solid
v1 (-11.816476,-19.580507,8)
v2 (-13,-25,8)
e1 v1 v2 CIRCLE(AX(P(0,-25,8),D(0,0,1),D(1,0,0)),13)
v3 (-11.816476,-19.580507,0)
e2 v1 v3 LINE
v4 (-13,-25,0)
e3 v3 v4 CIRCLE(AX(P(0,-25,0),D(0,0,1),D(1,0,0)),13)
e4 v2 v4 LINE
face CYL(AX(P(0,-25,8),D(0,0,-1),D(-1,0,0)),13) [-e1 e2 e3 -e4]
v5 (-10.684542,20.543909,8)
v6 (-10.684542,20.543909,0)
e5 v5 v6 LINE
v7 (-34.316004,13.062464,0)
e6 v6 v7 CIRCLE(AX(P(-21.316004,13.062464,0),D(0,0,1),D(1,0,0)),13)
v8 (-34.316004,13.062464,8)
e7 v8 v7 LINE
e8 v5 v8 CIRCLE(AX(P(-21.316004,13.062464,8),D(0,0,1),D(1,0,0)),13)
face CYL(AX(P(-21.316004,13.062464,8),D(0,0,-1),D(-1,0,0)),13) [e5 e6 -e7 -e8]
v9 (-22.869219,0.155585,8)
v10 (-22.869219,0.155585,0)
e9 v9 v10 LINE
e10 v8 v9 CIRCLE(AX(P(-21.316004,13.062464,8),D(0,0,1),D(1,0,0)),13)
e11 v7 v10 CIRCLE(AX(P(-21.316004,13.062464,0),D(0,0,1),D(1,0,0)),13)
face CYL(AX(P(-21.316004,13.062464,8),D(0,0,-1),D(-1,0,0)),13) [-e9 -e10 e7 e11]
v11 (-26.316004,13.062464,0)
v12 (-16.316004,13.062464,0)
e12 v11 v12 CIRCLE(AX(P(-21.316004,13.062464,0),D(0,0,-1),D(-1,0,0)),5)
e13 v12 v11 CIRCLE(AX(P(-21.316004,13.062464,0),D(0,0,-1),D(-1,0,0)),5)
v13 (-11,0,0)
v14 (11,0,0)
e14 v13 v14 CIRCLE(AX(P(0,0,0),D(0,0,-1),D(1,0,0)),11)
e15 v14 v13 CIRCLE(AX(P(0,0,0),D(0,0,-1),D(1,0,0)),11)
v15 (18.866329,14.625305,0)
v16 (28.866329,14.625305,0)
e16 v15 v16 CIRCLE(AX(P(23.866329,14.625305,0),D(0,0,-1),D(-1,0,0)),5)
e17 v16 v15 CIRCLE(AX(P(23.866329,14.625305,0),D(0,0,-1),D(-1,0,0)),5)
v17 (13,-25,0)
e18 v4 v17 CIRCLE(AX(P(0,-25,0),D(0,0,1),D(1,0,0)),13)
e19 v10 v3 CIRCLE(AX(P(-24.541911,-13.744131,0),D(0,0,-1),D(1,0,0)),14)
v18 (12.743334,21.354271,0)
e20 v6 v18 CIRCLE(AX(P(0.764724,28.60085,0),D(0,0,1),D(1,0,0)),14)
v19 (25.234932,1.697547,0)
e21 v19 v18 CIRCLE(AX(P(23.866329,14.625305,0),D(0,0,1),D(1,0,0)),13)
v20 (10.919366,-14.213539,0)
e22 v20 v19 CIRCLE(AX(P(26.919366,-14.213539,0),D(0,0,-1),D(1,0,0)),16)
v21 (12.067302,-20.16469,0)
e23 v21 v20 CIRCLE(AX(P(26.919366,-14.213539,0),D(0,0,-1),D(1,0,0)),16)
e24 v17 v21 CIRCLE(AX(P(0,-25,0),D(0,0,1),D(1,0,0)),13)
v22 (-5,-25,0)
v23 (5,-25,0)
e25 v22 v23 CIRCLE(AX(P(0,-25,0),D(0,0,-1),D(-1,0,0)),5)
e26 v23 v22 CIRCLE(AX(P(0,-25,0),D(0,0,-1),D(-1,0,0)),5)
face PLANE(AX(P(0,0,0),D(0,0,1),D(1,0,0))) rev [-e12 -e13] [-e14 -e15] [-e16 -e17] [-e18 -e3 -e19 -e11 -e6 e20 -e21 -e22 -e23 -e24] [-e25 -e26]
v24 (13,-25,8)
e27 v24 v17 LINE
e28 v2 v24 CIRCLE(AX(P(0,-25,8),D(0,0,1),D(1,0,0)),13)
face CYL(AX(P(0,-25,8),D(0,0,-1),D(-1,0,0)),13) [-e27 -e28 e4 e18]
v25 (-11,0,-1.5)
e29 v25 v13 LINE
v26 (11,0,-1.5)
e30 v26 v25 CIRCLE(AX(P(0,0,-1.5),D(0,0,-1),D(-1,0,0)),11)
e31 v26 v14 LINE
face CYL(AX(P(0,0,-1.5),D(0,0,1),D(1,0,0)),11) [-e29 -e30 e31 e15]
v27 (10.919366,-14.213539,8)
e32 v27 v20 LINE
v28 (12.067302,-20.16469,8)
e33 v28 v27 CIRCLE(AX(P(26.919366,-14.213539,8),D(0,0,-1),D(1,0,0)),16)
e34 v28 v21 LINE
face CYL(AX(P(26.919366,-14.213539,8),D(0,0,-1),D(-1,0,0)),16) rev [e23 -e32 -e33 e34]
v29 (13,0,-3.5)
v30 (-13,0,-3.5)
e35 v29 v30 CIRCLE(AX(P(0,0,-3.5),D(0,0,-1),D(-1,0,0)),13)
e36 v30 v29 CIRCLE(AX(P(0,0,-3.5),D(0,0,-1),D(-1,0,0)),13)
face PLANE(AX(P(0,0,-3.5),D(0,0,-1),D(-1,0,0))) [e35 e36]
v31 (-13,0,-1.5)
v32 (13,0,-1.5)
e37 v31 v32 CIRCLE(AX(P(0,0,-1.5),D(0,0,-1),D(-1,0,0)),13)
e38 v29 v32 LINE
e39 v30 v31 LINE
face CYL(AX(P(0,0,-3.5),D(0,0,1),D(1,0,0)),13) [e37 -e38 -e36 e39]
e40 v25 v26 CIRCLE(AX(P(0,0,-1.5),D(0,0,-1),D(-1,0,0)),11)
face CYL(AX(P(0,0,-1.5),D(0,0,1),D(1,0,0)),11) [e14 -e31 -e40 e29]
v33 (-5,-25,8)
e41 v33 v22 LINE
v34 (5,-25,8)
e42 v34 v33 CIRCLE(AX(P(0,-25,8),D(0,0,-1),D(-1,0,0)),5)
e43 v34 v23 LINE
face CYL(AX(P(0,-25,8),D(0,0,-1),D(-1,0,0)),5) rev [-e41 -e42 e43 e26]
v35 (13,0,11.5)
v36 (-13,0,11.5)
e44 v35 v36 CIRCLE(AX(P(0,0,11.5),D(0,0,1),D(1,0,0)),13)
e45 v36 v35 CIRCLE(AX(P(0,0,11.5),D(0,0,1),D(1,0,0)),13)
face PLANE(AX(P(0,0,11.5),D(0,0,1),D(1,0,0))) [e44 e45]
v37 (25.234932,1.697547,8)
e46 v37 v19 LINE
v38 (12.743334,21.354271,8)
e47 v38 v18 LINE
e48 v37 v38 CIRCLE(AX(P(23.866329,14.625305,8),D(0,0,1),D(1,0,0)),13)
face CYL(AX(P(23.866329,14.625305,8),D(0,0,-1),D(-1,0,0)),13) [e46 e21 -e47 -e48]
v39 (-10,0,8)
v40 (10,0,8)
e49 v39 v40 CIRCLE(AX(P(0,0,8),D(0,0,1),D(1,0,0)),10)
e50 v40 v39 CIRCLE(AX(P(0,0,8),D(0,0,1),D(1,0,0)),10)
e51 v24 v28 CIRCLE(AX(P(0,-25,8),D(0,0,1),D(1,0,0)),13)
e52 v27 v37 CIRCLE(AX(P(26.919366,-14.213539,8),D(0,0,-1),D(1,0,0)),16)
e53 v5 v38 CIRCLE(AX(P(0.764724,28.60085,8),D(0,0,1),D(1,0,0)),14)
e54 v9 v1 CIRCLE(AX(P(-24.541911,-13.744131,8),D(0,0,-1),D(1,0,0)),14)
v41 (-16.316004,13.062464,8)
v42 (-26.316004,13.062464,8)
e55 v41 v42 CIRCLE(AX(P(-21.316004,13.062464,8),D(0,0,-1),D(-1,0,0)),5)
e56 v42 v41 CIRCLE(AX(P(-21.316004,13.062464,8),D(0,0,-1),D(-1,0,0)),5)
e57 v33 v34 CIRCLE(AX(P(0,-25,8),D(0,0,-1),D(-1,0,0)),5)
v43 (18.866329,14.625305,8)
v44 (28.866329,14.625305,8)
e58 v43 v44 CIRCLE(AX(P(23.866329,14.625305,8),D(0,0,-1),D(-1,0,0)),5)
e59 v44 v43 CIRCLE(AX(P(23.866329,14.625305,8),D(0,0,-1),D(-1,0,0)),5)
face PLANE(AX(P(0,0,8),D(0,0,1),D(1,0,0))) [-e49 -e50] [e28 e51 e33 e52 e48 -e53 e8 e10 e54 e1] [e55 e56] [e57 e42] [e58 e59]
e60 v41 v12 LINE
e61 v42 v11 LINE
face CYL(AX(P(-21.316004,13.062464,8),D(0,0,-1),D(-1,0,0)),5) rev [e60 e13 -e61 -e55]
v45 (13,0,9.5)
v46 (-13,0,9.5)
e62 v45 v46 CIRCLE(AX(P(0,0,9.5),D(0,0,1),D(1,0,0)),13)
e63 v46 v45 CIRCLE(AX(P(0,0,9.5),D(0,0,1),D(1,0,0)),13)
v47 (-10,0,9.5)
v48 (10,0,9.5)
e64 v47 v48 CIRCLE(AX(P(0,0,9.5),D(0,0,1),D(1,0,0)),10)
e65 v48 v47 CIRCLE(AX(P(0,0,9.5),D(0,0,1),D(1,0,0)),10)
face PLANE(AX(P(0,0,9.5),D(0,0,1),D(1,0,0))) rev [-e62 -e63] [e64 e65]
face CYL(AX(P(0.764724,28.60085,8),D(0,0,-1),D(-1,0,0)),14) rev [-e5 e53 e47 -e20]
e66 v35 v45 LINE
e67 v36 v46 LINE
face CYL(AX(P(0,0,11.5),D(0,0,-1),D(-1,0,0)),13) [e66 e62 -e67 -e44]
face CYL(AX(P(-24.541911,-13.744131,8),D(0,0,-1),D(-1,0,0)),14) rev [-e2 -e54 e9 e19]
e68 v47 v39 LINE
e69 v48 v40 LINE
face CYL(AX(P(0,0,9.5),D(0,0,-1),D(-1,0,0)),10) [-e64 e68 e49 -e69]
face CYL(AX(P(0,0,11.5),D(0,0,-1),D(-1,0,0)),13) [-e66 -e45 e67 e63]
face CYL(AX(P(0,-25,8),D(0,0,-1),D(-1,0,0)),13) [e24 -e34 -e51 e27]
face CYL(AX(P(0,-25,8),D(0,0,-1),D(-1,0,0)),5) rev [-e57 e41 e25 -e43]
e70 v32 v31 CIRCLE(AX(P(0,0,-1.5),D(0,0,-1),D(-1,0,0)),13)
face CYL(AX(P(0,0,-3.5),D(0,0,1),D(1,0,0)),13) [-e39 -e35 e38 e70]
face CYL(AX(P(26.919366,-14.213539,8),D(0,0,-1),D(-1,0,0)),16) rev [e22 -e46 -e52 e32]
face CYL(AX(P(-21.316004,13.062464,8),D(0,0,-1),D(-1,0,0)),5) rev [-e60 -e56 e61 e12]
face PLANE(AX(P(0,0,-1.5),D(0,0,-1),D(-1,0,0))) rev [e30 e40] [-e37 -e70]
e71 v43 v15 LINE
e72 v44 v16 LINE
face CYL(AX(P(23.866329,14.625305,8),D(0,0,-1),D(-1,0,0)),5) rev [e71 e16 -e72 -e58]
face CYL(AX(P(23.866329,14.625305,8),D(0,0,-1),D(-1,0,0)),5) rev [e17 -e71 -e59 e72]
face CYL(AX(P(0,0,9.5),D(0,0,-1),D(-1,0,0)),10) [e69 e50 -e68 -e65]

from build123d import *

# Parameters (mm, degrees)
SPINNER_BODY_DEPTH             = 8
HUB_BOSS_10_SKETCH_R           = 10
HUB_BOSS_10_DEPTH              = 1.5
HUB_BOSS_11_SKETCH_R           = 11
HUB_BOSS_11_DEPTH              = 1.5
HUB_CAP_13_ON_11_BOSS_SKETCH_R = 13
HUB_CAP_13_ON_11_BOSS_DEPTH    = 2
HUB_START                      = 2
HUB_CAP_13_ON_10_BOSS_SKETCH_R = 13
HUB_CAP_13_ON_10_BOSS_DEPTH    = 2
LOBE_HOLES_3X_10_SKETCH_R      = 10
LOBE_HOLES_3X_10_DEPTH         = 8
LOBE_RINGS_3X_10_9_SKETCH_R    = 10
LOBE_RINGS_3X_10_9_SKETCH_R_2  = 9
LOBE_RINGS_3X_10_9_DEPTH       = 8
LOBE_RINGS_3X_9_6_SKETCH_R     = 9
LOBE_RINGS_3X_9_6_SKETCH_R_2   = 6
LOBE_RINGS_3X_9_6_DEPTH        = 8
LOBE_RINGS_3X_6_5_SKETCH_R     = 6
LOBE_RINGS_3X_6_5_SKETCH_R_2   = 5
LOBE_RINGS_3X_6_5_DEPTH        = 8


with BuildPart() as part:
    # Spinner Body Sketch → Spinner Body (new body)
    with BuildSketch(Plane.XY):
        with BuildLine():
            ThreePointArc((-11.816475763, -19.580507354), (-0.317877053, -37.996113041), (12.067302022, -20.164690091))
            ThreePointArc((12.067302022, -20.164690091), (13.213407519, -5.958437932), (25.234931886, 1.697547316))
            ThreePointArc((25.234931886, 1.697547316), (34.838281601, 21.597841349), (12.74333417, 21.35427128))
            ThreePointArc((12.74333417, 21.35427128), (1.248689911, 14.609217628), (-10.684542323, 20.543909185))
            ThreePointArc((-10.684542323, 20.543909185), (-32.475062427, 19.731453355), (-22.869218634, 0.155585152))
            ThreePointArc((-22.869218634, 0.155585152), (-12.326967101, -6.903433276), (-11.816475763, -19.580507354))
        make_face()
    extrude(amount=SPINNER_BODY_DEPTH)

    # Hub Boss Ø10 Sketch → Hub Boss Ø10 (add)
    with BuildSketch(Plane.XY.offset(8)):
        Circle(HUB_BOSS_10_SKETCH_R)
    extrude(amount=HUB_BOSS_10_DEPTH)

    # Hub Boss Ø11 Sketch → Hub Boss Ø11 (add)
    with BuildSketch(Plane(origin=(0, 0, 0), x_dir=(-1, 0, 0), z_dir=(0, 0, -1))):
        with Locations(Location((0, 0, 0), (0, 0, 180))):
            Circle(HUB_BOSS_11_SKETCH_R)
    extrude(amount=HUB_BOSS_11_DEPTH)

    # Hub Cap Ø13 on Ø11 Boss Sketch → Hub Cap Ø13 on Ø11 Boss (add)
    with BuildSketch(Plane(origin=(0, 0, -1.5), x_dir=(-1, 0, 0), z_dir=(0, 0, -1))):
        Circle(HUB_CAP_13_ON_11_BOSS_SKETCH_R)
    extrude(amount=HUB_CAP_13_ON_11_BOSS_DEPTH)

    # Hub Cap Ø13 on Ø10 Boss Sketch → Hub Cap Ø13 on Ø10 Boss (add)
    with BuildSketch(Plane.XY.offset(9.5).offset(HUB_START)):
        with Locations(Location((0, 0, 0), (0, 0, 180))):
            Circle(HUB_CAP_13_ON_10_BOSS_SKETCH_R)
    extrude(amount=-HUB_CAP_13_ON_10_BOSS_DEPTH)

    # Lobe Holes 3xØ10 Sketch → Lobe Holes 3xØ10 (cut)
    with BuildSketch(Plane(origin=(0, 0, 0), x_dir=(-1, 0, 0), z_dir=(0, 0, -1))):
        with Locations((-23.866329129, 14.6253053)):
            Circle(LOBE_HOLES_3X_10_SKETCH_R)
        with Locations((21.316004109, 13.062464118)):
            Circle(LOBE_HOLES_3X_10_SKETCH_R)
        with Locations((0, -25)):
            Circle(LOBE_HOLES_3X_10_SKETCH_R)
    extrude(amount=-LOBE_HOLES_3X_10_DEPTH, mode=Mode.SUBTRACT)

    # Lobe Rings 3xØ10-Ø9 Sketch → Lobe Rings 3xØ10-Ø9 (add)
    # profile 1 of 3: a face of its own
    with BuildSketch(Plane(origin=(0, 0, 0), x_dir=(-1, 0, 0), z_dir=(0, 0, -1))):
        with Locations((-23.866329129, 14.6253053)):
            Circle(LOBE_RINGS_3X_10_9_SKETCH_R)
        with Locations((-23.866329129, 14.6253053)):
            Circle(LOBE_RINGS_3X_10_9_SKETCH_R_2, mode=Mode.SUBTRACT)
    # profile 2 of 3: a face of its own
    with BuildSketch(Plane(origin=(0, 0, 0), x_dir=(-1, 0, 0), z_dir=(0, 0, -1))):
        with Locations((21.316004109, 13.062464118)):
            Circle(LOBE_RINGS_3X_10_9_SKETCH_R)
        with Locations((21.316004109, 13.062464118)):
            Circle(LOBE_RINGS_3X_10_9_SKETCH_R_2, mode=Mode.SUBTRACT)
    # profile 3 of 3: a face of its own
    with BuildSketch(Plane(origin=(0, 0, 0), x_dir=(-1, 0, 0), z_dir=(0, 0, -1))):
        with Locations((0, -25)):
            Circle(LOBE_RINGS_3X_10_9_SKETCH_R)
        with Locations((0, -25)):
            Circle(LOBE_RINGS_3X_10_9_SKETCH_R_2, mode=Mode.SUBTRACT)
    extrude(amount=-LOBE_RINGS_3X_10_9_DEPTH)

    # Lobe Rings 3xØ9-Ø6 Sketch → Lobe Rings 3xØ9-Ø6 (add)
    # profile 1 of 3: a face of its own
    with BuildSketch(Plane(origin=(0, 0, 0), x_dir=(-1, 0, 0), z_dir=(0, 0, -1))):
        with Locations((-23.866329129, 14.6253053)):
            Circle(LOBE_RINGS_3X_9_6_SKETCH_R)
        with Locations((-23.866329129, 14.6253053)):
            Circle(LOBE_RINGS_3X_9_6_SKETCH_R_2, mode=Mode.SUBTRACT)
    # profile 2 of 3: a face of its own
    with BuildSketch(Plane(origin=(0, 0, 0), x_dir=(-1, 0, 0), z_dir=(0, 0, -1))):
        with Locations((21.316004109, 13.062464118)):
            Circle(LOBE_RINGS_3X_9_6_SKETCH_R)
        with Locations((21.316004109, 13.062464118)):
            Circle(LOBE_RINGS_3X_9_6_SKETCH_R_2, mode=Mode.SUBTRACT)
    # profile 3 of 3: a face of its own
    with BuildSketch(Plane(origin=(0, 0, 0), x_dir=(-1, 0, 0), z_dir=(0, 0, -1))):
        with Locations((0, -25)):
            Circle(LOBE_RINGS_3X_9_6_SKETCH_R)
        with Locations((0, -25)):
            Circle(LOBE_RINGS_3X_9_6_SKETCH_R_2, mode=Mode.SUBTRACT)
    extrude(amount=-LOBE_RINGS_3X_9_6_DEPTH)

    # Lobe Rings 3xØ6-Ø5 Sketch → Lobe Rings 3xØ6-Ø5 (add)
    # profile 1 of 3: a face of its own
    with BuildSketch(Plane(origin=(0, 0, 0), x_dir=(-1, 0, 0), z_dir=(0, 0, -1))):
        with Locations((-23.866329129, 14.6253053)):
            Circle(LOBE_RINGS_3X_6_5_SKETCH_R)
        with Locations((-23.866329129, 14.6253053)):
            Circle(LOBE_RINGS_3X_6_5_SKETCH_R_2, mode=Mode.SUBTRACT)
    # profile 2 of 3: a face of its own
    with BuildSketch(Plane(origin=(0, 0, 0), x_dir=(-1, 0, 0), z_dir=(0, 0, -1))):
        with Locations((21.316004109, 13.062464118)):
            Circle(LOBE_RINGS_3X_6_5_SKETCH_R)
        with Locations((21.316004109, 13.062464118)):
            Circle(LOBE_RINGS_3X_6_5_SKETCH_R_2, mode=Mode.SUBTRACT)
    # profile 3 of 3: a face of its own
    with BuildSketch(Plane(origin=(0, 0, 0), x_dir=(-1, 0, 0), z_dir=(0, 0, -1))):
        with Locations((0, -25)):
            Circle(LOBE_RINGS_3X_6_5_SKETCH_R)
        with Locations((0, -25)):
            Circle(LOBE_RINGS_3X_6_5_SKETCH_R_2, mode=Mode.SUBTRACT)
    extrude(amount=-LOBE_RINGS_3X_6_5_DEPTH)


solid = part.part
